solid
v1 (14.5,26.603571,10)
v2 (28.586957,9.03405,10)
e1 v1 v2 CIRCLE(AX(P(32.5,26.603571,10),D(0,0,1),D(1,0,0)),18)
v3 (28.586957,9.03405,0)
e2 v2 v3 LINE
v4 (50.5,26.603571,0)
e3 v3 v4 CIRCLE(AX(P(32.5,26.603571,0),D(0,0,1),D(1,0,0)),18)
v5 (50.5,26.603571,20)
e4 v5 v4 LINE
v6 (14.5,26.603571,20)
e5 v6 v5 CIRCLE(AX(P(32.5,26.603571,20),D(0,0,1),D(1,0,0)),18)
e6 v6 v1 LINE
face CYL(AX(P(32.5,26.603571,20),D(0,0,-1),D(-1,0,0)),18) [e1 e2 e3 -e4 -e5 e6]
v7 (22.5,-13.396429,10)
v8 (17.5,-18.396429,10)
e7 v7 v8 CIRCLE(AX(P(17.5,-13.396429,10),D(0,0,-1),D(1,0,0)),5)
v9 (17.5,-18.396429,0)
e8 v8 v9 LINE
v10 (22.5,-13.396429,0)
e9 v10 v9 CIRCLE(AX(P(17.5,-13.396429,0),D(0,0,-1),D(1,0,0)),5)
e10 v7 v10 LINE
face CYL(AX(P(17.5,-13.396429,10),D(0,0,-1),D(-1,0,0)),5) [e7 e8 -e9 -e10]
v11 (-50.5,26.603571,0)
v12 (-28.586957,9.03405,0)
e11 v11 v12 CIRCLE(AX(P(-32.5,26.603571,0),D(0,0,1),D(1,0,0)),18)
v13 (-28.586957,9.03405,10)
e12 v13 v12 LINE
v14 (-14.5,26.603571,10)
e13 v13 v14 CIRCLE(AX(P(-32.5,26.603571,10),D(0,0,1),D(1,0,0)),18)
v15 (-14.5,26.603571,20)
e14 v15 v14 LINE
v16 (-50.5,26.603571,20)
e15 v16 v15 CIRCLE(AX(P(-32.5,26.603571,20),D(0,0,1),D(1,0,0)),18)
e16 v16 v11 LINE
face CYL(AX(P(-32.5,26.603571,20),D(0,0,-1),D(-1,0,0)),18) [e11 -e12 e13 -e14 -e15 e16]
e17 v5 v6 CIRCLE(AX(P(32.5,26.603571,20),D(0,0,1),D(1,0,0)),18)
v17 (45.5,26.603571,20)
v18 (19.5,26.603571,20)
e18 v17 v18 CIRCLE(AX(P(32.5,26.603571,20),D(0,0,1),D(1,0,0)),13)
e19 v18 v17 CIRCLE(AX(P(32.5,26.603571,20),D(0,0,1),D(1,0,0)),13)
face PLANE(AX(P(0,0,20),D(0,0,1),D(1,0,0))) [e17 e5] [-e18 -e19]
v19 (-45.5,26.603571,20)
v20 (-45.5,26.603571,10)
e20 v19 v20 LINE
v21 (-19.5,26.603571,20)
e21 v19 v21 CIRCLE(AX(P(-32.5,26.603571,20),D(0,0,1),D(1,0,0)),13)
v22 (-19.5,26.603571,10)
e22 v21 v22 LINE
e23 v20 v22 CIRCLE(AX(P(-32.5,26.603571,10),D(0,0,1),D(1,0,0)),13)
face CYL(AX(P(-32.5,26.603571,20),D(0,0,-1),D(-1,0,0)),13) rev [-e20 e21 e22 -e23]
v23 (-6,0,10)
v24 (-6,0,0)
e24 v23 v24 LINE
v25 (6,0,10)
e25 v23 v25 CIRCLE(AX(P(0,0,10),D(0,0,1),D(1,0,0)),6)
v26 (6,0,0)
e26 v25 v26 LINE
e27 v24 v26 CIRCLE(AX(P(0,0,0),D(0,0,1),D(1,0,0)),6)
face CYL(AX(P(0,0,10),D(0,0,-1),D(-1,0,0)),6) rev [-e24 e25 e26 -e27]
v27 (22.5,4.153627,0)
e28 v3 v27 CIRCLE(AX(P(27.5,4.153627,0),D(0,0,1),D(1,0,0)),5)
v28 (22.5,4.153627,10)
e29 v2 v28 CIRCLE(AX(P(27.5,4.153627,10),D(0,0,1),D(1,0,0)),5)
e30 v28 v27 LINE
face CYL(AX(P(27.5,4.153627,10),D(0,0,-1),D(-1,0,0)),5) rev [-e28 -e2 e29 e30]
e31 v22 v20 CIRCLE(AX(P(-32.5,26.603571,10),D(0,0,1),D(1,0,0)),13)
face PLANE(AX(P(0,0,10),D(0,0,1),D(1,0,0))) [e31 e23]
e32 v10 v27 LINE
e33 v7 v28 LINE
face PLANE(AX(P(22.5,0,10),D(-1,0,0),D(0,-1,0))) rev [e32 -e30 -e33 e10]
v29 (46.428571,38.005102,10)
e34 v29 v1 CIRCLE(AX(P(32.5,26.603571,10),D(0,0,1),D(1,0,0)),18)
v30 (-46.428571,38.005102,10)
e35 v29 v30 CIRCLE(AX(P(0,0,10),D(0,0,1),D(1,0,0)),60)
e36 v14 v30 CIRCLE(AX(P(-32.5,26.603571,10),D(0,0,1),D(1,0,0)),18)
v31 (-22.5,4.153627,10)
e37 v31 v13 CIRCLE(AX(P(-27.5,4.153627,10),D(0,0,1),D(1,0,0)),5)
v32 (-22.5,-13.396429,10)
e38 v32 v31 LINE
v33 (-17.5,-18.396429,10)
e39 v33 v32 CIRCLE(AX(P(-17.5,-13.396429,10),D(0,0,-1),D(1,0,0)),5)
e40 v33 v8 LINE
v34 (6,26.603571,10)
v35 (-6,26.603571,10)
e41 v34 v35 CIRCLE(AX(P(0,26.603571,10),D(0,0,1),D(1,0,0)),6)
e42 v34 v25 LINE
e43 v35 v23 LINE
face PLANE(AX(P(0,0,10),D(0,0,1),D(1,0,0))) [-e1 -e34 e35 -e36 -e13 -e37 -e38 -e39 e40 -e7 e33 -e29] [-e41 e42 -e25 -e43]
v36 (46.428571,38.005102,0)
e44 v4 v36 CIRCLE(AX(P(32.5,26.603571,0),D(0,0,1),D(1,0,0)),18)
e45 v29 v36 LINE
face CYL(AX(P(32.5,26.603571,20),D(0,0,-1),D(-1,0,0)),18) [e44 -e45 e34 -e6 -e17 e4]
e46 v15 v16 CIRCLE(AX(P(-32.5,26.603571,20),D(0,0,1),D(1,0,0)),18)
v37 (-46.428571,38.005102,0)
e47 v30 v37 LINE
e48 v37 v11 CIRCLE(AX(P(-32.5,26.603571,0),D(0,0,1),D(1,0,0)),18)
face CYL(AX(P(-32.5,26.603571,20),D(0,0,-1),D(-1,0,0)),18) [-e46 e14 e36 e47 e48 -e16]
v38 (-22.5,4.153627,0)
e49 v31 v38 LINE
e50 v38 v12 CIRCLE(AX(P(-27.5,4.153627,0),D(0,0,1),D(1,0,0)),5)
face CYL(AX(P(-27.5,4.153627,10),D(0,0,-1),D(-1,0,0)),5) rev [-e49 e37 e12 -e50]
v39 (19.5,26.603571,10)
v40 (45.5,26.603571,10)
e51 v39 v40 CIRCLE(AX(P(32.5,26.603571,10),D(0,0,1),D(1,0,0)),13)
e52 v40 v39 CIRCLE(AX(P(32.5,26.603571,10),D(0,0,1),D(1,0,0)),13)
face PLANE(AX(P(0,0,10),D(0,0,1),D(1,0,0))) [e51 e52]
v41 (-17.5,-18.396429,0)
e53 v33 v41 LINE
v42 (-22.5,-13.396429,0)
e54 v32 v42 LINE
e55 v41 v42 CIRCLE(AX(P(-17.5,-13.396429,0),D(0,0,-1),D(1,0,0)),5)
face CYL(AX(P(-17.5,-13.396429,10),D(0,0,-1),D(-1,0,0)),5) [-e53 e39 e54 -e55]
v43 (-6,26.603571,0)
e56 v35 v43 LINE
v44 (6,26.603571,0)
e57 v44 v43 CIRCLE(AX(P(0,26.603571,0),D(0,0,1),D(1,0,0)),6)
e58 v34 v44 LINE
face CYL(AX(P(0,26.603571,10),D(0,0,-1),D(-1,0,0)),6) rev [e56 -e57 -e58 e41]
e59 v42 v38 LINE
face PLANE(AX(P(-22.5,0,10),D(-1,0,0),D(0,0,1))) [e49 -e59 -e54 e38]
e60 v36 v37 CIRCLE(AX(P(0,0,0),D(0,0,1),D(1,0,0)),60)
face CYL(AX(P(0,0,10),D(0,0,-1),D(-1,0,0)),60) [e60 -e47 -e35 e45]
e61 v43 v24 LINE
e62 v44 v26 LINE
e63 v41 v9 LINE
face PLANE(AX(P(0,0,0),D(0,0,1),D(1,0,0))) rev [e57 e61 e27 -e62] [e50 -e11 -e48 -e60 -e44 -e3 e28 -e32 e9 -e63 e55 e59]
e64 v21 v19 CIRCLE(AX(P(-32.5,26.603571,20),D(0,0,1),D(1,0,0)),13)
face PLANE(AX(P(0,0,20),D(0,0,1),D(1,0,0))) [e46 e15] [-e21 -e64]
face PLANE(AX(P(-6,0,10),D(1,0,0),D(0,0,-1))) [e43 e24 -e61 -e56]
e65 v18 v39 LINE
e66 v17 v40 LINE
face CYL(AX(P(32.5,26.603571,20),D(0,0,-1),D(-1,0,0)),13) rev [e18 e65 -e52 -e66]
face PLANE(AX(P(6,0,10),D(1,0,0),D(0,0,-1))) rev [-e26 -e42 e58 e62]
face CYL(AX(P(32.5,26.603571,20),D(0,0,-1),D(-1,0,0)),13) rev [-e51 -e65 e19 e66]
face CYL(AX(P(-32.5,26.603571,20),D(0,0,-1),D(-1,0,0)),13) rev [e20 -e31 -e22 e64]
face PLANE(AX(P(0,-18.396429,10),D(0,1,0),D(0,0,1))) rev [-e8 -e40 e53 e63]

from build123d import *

# Parameters (mm, degrees)
BASE_PLATE_10MM_DEPTH    = 10
BRACKET_PROFILE_SKETCH_R = 13
BASE_PLATE_10MM_2_DEPTH  = 10
BASE_PLATE_10MM_3_DEPTH  = 10
SKETCH1_3_R              = 18
SKETCH1_3_R_2            = 13
HUB_BOSSES_20MM_DEPTH    = 20


with BuildPart() as part:
    # Bracket Profile Sketch → Base Plate 10mm (new body)
    with BuildSketch(Plane.XY):
        with BuildLine():
            ThreePointArc((-22.5, -13.396428811), (-21.035533906, -16.931962717), (-17.5, -18.396428811))
            Line((-17.5, -18.396428811), (17.5, -18.396428811))
            ThreePointArc((17.5, -18.396428811), (21.035533906, -16.931962717), (22.5, -13.396428811))
            Line((22.5, -13.396428811), (22.5, 4.153626868))
            ThreePointArc((22.5, 4.153626868), (24.37228383, 8.054574389), (28.586956623, 9.034049524))
            ThreePointArc((28.586956623, 9.034049524), (17.173285852, 36.042418229), (46.428571429, 38.005101698))
            ThreePointArc((46.428571429, 38.005101698), (0, 60), (-46.428571429, 38.005101698))
            ThreePointArc((-46.428571429, 38.005101698), (-26.446665618, 43.555182996), (-14.5, 26.603571189))
            ThreePointArc((-14.5, 26.603571189), (-18.456589043, 15.34379283), (-28.586956522, 9.034049547))
            ThreePointArc((-28.586956522, 9.034049547), (-24.372283789, 8.054574356), (-22.5, 4.153626868))
            Line((-22.5, 4.153626868), (-22.5, -13.396428811))
        make_face()
        with BuildLine():
            Line((-6, 0), (-6, 26.603571189))
            ThreePointArc((-6, 26.603571189), (0, 32.603571189), (6, 26.603571189))
            Line((6, 26.603571189), (6, 0))
            ThreePointArc((6, 0), (0, -6), (-6, 0))
        make_face(mode=Mode.SUBTRACT)
    extrude(amount=BASE_PLATE_10MM_DEPTH)



with BuildPart() as body_2:
    # Bracket Profile Sketch → Base Plate 10mm 2 (new body)
    with BuildSketch(Plane.XY):
        with Locations((-32.5, 26.603571189)):
            Circle(BRACKET_PROFILE_SKETCH_R)
    extrude(amount=BASE_PLATE_10MM_2_DEPTH)


with BuildPart() as body_3:
    # Bracket Profile Sketch → Base Plate 10mm 3 (new body)
    with BuildSketch(Plane.XY):
        with Locations((32.5, 26.603571189)):
            Circle(BRACKET_PROFILE_SKETCH_R)
    extrude(amount=BASE_PLATE_10MM_3_DEPTH)


with BuildPart() as part_1:
    add(part.part)

    add(body_2.part)  # Hub Bosses 20mm merges body 2

    add(body_3.part)  # Hub Bosses 20mm merges body 3
    # Sketch1_3 → Hub Bosses 20mm (add)
    # profile 1 of 2: a face of its own
    with BuildSketch(Plane.XY):
        with Locations(Location((-32.5, 26.603571189, 0), (0, 0, 140.697224227))):
            Circle(SKETCH1_3_R)
        with Locations((-32.5, 26.603571189)):
            Circle(SKETCH1_3_R_2, mode=Mode.SUBTRACT)
    # profile 2 of 2: a face of its own
    with BuildSketch(Plane.XY):
        with Locations(Location((32.5, 26.603571189, 0), (0, 0, 257.444142201))):
            Circle(SKETCH1_3_R)
        with Locations((32.5, 26.603571189)):
            Circle(SKETCH1_3_R_2, mode=Mode.SUBTRACT)
    extrude(amount=HUB_BOSSES_20MM_DEPTH)


solid = part_1.part
